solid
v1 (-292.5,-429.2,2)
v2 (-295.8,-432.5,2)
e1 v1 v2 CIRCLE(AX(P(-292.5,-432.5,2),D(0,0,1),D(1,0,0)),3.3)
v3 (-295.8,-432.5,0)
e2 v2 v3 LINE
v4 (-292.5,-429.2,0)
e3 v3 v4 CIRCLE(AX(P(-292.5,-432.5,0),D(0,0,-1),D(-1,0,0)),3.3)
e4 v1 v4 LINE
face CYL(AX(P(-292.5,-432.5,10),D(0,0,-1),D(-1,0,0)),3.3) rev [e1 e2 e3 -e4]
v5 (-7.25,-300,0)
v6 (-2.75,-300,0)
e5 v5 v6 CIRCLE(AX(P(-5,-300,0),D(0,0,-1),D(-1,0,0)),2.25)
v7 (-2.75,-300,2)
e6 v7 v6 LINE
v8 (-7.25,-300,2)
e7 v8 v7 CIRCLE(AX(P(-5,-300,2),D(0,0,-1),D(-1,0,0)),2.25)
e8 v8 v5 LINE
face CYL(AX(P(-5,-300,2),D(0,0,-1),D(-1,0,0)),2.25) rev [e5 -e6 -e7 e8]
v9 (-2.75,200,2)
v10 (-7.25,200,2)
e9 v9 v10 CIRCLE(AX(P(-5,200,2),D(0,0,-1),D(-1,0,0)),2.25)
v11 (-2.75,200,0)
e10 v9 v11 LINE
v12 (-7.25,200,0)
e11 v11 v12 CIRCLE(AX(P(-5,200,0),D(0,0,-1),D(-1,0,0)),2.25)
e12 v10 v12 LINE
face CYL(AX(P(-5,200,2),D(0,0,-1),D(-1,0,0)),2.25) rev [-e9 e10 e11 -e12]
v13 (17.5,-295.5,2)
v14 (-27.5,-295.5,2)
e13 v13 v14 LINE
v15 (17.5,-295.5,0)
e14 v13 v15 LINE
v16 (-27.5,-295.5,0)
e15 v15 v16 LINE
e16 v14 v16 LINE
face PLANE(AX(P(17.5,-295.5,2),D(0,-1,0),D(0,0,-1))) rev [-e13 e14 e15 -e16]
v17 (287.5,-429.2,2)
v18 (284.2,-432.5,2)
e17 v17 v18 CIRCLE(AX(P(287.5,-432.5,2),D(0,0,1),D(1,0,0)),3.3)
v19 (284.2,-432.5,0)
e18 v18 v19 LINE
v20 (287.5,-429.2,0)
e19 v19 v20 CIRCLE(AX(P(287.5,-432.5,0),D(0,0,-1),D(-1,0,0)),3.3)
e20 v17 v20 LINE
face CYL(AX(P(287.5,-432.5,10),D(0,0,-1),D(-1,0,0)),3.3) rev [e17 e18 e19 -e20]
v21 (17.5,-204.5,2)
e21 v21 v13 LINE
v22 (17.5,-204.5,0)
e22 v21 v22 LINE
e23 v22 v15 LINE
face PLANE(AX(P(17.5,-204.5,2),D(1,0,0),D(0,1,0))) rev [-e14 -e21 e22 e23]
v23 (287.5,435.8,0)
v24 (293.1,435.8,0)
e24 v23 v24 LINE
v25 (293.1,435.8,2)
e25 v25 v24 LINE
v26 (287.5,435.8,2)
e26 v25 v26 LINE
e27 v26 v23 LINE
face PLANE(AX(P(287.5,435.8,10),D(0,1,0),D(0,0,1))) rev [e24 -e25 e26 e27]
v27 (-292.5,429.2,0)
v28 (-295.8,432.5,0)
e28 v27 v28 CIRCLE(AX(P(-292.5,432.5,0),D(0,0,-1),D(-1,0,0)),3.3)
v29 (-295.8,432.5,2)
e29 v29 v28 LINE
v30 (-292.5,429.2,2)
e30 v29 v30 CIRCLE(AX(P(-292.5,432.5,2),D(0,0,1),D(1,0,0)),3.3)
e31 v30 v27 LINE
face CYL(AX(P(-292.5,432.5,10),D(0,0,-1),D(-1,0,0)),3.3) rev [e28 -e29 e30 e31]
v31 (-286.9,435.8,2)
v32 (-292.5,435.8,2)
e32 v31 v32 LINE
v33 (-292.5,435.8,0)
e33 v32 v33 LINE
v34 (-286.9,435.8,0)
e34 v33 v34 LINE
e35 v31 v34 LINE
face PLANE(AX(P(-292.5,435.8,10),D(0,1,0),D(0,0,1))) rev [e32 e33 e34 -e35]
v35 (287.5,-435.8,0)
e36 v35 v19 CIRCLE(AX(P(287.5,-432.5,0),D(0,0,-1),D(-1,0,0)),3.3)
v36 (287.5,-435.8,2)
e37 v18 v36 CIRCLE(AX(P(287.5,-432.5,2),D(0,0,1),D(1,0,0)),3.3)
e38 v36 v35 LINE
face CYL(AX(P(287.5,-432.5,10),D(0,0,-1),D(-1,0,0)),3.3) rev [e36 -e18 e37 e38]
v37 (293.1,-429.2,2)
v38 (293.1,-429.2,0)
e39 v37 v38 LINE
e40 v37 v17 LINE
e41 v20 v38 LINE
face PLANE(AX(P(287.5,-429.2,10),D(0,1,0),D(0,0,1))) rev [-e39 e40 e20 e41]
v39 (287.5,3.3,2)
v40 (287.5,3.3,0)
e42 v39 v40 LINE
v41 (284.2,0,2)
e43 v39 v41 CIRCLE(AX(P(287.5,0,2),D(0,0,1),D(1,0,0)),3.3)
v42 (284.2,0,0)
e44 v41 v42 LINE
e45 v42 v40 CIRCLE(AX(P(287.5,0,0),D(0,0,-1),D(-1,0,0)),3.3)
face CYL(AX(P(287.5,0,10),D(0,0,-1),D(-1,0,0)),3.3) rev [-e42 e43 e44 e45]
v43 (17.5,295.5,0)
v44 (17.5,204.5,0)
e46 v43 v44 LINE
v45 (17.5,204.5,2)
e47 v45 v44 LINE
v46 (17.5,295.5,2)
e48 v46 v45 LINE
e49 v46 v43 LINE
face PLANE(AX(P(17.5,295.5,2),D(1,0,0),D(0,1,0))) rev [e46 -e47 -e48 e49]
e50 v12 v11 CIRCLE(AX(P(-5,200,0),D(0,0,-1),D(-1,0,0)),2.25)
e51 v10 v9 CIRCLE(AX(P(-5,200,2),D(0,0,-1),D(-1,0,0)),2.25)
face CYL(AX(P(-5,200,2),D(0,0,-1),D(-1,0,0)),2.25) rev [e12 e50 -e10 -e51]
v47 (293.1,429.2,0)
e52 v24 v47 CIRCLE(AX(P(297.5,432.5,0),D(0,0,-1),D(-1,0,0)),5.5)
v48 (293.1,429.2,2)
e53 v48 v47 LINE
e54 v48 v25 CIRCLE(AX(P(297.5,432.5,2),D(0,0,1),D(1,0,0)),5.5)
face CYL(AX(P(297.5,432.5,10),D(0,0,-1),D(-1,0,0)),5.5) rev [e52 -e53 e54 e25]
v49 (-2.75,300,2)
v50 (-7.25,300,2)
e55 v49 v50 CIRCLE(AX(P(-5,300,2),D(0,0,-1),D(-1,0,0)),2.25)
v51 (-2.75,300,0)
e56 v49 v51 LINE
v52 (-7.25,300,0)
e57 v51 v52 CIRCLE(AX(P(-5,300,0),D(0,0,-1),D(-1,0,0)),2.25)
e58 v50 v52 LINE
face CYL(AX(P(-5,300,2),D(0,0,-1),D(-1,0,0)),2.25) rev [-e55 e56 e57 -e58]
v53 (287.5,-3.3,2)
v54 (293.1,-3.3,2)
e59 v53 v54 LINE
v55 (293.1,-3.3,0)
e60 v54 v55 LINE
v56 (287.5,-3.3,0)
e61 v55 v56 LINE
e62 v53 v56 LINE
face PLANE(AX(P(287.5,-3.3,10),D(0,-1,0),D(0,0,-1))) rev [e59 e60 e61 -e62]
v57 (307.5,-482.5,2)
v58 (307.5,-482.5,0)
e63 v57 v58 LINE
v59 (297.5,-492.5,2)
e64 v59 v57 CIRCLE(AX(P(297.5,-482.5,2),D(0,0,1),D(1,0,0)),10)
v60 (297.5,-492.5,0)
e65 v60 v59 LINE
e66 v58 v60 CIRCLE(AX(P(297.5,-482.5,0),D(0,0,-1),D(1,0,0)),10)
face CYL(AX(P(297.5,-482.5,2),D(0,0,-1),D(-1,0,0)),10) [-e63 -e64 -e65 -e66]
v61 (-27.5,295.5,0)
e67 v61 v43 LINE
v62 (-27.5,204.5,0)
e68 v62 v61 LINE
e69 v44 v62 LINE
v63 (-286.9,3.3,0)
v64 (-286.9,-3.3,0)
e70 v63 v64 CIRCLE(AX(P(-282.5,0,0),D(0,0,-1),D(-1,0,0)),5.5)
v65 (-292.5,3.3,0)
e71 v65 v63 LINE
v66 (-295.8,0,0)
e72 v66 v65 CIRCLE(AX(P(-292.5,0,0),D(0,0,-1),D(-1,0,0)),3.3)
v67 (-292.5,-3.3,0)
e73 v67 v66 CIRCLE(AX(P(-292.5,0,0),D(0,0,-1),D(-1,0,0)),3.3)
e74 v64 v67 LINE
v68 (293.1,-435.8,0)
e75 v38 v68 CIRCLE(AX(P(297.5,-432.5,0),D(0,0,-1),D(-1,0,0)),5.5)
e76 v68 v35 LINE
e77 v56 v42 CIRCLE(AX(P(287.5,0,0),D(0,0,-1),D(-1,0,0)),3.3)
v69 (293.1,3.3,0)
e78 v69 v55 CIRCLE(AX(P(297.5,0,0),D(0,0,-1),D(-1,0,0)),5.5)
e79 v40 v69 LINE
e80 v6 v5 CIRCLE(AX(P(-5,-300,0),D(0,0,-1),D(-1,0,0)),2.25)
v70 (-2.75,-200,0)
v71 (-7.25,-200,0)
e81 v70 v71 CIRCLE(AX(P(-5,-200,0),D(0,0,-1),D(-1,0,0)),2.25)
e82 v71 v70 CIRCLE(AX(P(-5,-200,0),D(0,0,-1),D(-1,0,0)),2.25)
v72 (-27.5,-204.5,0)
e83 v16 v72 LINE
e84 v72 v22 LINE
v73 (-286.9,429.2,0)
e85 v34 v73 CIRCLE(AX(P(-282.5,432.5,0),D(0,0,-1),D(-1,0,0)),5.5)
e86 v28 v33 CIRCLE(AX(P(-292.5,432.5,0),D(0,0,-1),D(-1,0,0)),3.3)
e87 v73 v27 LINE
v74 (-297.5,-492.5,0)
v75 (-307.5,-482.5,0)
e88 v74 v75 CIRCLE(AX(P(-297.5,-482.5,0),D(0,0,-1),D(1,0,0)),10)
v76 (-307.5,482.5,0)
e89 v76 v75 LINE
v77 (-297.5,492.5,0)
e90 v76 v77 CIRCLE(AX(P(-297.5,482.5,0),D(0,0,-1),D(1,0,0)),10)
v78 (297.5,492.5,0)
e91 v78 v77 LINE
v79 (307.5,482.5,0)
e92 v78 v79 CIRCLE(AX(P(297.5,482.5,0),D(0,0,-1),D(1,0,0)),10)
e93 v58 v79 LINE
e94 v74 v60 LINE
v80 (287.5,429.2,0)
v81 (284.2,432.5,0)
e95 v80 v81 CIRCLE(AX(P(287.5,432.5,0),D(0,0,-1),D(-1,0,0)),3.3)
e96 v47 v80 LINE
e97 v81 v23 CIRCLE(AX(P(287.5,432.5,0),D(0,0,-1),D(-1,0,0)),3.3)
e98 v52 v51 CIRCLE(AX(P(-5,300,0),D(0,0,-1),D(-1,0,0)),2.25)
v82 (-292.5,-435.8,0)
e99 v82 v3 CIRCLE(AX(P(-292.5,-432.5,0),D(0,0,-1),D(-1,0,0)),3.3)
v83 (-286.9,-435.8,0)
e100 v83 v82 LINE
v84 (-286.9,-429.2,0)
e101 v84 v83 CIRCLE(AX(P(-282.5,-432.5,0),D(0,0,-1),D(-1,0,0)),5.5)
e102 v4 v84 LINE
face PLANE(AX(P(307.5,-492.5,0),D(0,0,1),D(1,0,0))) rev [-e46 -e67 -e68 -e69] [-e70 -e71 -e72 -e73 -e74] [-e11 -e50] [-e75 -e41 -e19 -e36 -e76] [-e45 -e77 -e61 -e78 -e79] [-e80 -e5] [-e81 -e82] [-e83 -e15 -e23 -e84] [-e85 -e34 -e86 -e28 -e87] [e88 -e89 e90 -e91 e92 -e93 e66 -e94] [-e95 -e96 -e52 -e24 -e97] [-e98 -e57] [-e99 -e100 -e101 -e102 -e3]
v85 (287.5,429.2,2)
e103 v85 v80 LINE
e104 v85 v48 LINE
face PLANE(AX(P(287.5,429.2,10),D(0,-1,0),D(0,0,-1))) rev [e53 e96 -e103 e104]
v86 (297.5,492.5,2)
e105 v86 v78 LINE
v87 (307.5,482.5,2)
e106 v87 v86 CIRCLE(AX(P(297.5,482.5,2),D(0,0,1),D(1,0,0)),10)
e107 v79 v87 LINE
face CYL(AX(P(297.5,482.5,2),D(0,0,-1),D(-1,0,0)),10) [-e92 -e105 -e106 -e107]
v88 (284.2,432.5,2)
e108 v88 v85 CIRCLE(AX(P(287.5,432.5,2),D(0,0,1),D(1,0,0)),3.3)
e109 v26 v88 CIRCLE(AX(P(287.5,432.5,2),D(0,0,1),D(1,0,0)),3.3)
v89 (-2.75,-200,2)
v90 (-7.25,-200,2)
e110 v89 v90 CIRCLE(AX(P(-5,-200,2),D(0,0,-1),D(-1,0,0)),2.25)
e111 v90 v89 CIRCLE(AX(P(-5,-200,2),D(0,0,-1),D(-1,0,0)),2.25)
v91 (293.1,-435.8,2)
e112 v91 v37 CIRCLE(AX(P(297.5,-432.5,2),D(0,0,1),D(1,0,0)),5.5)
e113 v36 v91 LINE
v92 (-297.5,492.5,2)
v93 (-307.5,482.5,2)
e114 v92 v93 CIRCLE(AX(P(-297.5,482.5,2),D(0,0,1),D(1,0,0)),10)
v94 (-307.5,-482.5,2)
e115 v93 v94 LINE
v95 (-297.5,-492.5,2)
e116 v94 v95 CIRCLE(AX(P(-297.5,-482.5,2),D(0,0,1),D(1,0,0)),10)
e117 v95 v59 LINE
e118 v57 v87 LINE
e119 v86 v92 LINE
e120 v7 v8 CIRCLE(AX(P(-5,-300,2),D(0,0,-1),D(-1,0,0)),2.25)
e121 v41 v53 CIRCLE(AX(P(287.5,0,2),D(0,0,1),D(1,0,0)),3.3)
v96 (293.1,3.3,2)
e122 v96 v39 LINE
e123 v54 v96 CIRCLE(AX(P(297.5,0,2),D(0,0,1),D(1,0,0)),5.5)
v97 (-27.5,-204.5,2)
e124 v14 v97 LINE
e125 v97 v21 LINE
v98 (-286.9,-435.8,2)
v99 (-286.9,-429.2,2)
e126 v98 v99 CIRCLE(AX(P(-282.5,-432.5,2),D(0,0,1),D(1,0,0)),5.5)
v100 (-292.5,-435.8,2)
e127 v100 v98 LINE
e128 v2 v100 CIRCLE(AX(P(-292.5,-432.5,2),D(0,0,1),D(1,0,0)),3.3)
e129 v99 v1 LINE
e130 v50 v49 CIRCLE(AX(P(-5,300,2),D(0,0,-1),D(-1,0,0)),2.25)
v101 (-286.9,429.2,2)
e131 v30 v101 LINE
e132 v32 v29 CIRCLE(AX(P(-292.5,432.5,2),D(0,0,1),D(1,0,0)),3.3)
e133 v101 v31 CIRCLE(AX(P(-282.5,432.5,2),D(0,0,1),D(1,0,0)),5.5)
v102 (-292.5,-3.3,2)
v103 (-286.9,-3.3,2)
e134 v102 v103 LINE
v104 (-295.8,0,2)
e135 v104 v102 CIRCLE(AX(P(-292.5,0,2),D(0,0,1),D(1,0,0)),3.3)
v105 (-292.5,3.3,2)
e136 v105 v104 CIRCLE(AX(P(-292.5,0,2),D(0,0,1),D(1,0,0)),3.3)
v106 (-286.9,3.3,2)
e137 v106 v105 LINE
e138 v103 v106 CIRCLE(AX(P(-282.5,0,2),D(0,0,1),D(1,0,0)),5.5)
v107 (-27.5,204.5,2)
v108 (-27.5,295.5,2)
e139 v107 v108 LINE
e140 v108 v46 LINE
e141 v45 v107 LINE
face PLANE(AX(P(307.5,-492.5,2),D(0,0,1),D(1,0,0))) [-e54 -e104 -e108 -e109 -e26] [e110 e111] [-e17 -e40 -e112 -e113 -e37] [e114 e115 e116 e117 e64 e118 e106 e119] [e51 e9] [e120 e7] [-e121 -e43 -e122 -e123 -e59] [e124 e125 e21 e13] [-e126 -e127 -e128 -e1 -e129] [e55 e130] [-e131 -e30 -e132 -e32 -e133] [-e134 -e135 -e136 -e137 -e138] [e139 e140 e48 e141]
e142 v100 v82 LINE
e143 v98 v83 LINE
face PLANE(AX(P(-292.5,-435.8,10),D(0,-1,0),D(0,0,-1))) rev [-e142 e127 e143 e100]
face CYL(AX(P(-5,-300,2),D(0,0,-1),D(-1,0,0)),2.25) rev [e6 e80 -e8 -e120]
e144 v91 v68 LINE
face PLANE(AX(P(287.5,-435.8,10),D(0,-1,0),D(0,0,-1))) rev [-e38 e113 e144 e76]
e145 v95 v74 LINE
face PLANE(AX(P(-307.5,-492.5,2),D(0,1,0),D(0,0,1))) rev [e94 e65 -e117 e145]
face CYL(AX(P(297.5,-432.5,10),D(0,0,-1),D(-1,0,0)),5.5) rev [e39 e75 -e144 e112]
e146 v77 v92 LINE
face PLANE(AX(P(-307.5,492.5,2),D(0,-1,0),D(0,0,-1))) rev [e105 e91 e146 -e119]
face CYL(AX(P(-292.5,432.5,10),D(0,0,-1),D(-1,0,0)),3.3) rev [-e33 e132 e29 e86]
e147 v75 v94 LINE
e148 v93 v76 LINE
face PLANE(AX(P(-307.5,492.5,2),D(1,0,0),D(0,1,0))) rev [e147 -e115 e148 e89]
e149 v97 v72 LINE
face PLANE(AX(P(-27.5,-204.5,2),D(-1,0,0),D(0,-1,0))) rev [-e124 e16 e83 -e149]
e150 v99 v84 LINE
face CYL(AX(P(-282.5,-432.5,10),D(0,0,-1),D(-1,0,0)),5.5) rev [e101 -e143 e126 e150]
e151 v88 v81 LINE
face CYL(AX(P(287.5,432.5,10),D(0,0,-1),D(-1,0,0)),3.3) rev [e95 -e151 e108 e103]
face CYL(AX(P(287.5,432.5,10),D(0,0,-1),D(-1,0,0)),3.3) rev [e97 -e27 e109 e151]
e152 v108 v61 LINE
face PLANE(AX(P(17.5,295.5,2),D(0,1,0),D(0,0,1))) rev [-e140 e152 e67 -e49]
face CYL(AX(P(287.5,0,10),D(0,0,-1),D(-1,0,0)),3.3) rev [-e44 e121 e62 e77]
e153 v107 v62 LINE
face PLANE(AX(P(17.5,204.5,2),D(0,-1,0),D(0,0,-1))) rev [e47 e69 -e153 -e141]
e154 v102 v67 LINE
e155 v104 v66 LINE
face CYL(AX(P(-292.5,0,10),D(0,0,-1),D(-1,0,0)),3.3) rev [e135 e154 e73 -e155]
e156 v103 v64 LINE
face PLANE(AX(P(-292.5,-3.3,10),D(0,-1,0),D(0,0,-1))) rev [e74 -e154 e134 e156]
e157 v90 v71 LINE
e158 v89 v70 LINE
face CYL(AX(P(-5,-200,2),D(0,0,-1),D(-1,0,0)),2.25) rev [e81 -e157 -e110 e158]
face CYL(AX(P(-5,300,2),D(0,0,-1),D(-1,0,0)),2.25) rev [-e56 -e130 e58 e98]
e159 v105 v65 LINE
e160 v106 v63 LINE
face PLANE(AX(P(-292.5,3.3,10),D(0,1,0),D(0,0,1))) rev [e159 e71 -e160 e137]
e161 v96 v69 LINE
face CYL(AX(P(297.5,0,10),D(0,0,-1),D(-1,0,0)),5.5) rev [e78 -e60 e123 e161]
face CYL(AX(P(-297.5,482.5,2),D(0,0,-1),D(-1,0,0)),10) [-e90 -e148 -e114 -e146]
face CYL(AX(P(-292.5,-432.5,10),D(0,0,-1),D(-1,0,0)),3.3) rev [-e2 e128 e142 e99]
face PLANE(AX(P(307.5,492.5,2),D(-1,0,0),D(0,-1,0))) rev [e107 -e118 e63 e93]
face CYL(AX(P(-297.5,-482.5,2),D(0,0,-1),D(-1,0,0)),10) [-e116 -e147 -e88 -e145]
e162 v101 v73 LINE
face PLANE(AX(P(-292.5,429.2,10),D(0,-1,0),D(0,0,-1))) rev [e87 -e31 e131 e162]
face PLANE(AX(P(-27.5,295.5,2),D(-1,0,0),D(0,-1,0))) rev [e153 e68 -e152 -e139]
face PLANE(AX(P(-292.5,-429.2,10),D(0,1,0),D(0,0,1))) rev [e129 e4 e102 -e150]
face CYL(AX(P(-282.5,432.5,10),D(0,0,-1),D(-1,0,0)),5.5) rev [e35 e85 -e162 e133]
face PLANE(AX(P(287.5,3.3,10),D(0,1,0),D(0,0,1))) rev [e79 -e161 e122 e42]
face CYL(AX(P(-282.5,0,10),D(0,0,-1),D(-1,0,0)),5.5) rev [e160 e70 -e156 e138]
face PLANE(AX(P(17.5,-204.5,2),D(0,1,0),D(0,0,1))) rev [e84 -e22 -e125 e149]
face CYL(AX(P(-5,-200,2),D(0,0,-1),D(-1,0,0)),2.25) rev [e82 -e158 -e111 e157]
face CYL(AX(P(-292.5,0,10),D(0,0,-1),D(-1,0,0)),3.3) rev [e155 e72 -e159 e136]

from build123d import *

# Parameters (mm, degrees)
SKETCH1_W            = 615
SKETCH1_H            = 985
BOSS_EXTRUDE1_DEPTH  = 2
SKETCH7_W            = 45
SKETCH7_H            = 91
CUT_EXTRUDE4_DEPTH   = 581.617343868
SKETCH8_R            = 2.25
CUT_EXTRUDE5_DEPTH   = 581.617343868
FILLET3_R            = 10
CUT_EXTRUDE6_DEPTH   = 10
LPATTERN1_COUNT      = 3
LPATTERN1_PITCH      = 432.5
LPATTERN1_COUNT_DIR2 = 2
LPATTERN1_PITCH_DIR2 = 580


with BuildPart() as part:
    # Sketch1 → Boss-Extrude1 (new body)
    with BuildSketch(Plane.XY):
        Rectangle(SKETCH1_W, SKETCH1_H)
    extrude(amount=BOSS_EXTRUDE1_DEPTH)

    # Sketch7 → Cut-Extrude4 (cut, through all)
    with BuildSketch(Plane(origin=(0, 0, 0), x_dir=(-1, 0, 0), z_dir=(0, 0, -1))):
        with Locations((5, 250)):
            Rectangle(SKETCH7_W, SKETCH7_H)
        with Locations((5, -250)):
            Rectangle(SKETCH7_W, SKETCH7_H)
    extrude(amount=-CUT_EXTRUDE4_DEPTH, mode=Mode.SUBTRACT)

    # Sketch8 → Cut-Extrude5 (cut, through all)
    with BuildSketch(Plane(origin=(0, 0, 0), x_dir=(-1, 0, 0), z_dir=(0, 0, -1))):
        with Locations((5, 300)):
            Circle(SKETCH8_R)
        with Locations((5, 200)):
            Circle(SKETCH8_R)
        with Locations((5, -200)):
            Circle(SKETCH8_R)
        with Locations((5, -300)):
            Circle(SKETCH8_R)
    extrude(amount=-CUT_EXTRUDE5_DEPTH, mode=Mode.SUBTRACT)

    # Fillet3
    fillet3_edges = [part.edges().sort_by_distance(p)[0] for p in [
        (307.5, -492.5, 1),
        (-307.5, -492.5, 1),
        (-307.5, 492.5, 1),
        (307.5, 492.5, 1),
    ]]
    fillet(fillet3_edges, radius=FILLET3_R)

    # Sketch10 → Cut-Extrude6 (cut)
    with BuildSketch(Plane(origin=(0, 0, 0), x_dir=(-1, 0, 0), z_dir=(0, 0, -1))):
        with BuildLine():
            Line((292.5, 435.8), (286.9, 435.8))
            ThreePointArc((286.9, 435.8), (277, 432.5), (286.9, 429.2))
            Line((286.9, 429.2), (292.5, 429.2))
            ThreePointArc((292.5, 429.2), (295.8, 432.5), (292.5, 435.8))
        make_face()
    cut_extrude6 = extrude(amount=-CUT_EXTRUDE6_DEPTH, mode=Mode.SUBTRACT)

    # LPattern1: Cut-Extrude6 3 × 2
    with Locations(*[(j * LPATTERN1_PITCH_DIR2, -i * LPATTERN1_PITCH, 0) for i in range(LPATTERN1_COUNT) for j in range(LPATTERN1_COUNT_DIR2) if (i, j) != (0, 0)]):
        add(cut_extrude6, mode=Mode.SUBTRACT)


solid = part.part
